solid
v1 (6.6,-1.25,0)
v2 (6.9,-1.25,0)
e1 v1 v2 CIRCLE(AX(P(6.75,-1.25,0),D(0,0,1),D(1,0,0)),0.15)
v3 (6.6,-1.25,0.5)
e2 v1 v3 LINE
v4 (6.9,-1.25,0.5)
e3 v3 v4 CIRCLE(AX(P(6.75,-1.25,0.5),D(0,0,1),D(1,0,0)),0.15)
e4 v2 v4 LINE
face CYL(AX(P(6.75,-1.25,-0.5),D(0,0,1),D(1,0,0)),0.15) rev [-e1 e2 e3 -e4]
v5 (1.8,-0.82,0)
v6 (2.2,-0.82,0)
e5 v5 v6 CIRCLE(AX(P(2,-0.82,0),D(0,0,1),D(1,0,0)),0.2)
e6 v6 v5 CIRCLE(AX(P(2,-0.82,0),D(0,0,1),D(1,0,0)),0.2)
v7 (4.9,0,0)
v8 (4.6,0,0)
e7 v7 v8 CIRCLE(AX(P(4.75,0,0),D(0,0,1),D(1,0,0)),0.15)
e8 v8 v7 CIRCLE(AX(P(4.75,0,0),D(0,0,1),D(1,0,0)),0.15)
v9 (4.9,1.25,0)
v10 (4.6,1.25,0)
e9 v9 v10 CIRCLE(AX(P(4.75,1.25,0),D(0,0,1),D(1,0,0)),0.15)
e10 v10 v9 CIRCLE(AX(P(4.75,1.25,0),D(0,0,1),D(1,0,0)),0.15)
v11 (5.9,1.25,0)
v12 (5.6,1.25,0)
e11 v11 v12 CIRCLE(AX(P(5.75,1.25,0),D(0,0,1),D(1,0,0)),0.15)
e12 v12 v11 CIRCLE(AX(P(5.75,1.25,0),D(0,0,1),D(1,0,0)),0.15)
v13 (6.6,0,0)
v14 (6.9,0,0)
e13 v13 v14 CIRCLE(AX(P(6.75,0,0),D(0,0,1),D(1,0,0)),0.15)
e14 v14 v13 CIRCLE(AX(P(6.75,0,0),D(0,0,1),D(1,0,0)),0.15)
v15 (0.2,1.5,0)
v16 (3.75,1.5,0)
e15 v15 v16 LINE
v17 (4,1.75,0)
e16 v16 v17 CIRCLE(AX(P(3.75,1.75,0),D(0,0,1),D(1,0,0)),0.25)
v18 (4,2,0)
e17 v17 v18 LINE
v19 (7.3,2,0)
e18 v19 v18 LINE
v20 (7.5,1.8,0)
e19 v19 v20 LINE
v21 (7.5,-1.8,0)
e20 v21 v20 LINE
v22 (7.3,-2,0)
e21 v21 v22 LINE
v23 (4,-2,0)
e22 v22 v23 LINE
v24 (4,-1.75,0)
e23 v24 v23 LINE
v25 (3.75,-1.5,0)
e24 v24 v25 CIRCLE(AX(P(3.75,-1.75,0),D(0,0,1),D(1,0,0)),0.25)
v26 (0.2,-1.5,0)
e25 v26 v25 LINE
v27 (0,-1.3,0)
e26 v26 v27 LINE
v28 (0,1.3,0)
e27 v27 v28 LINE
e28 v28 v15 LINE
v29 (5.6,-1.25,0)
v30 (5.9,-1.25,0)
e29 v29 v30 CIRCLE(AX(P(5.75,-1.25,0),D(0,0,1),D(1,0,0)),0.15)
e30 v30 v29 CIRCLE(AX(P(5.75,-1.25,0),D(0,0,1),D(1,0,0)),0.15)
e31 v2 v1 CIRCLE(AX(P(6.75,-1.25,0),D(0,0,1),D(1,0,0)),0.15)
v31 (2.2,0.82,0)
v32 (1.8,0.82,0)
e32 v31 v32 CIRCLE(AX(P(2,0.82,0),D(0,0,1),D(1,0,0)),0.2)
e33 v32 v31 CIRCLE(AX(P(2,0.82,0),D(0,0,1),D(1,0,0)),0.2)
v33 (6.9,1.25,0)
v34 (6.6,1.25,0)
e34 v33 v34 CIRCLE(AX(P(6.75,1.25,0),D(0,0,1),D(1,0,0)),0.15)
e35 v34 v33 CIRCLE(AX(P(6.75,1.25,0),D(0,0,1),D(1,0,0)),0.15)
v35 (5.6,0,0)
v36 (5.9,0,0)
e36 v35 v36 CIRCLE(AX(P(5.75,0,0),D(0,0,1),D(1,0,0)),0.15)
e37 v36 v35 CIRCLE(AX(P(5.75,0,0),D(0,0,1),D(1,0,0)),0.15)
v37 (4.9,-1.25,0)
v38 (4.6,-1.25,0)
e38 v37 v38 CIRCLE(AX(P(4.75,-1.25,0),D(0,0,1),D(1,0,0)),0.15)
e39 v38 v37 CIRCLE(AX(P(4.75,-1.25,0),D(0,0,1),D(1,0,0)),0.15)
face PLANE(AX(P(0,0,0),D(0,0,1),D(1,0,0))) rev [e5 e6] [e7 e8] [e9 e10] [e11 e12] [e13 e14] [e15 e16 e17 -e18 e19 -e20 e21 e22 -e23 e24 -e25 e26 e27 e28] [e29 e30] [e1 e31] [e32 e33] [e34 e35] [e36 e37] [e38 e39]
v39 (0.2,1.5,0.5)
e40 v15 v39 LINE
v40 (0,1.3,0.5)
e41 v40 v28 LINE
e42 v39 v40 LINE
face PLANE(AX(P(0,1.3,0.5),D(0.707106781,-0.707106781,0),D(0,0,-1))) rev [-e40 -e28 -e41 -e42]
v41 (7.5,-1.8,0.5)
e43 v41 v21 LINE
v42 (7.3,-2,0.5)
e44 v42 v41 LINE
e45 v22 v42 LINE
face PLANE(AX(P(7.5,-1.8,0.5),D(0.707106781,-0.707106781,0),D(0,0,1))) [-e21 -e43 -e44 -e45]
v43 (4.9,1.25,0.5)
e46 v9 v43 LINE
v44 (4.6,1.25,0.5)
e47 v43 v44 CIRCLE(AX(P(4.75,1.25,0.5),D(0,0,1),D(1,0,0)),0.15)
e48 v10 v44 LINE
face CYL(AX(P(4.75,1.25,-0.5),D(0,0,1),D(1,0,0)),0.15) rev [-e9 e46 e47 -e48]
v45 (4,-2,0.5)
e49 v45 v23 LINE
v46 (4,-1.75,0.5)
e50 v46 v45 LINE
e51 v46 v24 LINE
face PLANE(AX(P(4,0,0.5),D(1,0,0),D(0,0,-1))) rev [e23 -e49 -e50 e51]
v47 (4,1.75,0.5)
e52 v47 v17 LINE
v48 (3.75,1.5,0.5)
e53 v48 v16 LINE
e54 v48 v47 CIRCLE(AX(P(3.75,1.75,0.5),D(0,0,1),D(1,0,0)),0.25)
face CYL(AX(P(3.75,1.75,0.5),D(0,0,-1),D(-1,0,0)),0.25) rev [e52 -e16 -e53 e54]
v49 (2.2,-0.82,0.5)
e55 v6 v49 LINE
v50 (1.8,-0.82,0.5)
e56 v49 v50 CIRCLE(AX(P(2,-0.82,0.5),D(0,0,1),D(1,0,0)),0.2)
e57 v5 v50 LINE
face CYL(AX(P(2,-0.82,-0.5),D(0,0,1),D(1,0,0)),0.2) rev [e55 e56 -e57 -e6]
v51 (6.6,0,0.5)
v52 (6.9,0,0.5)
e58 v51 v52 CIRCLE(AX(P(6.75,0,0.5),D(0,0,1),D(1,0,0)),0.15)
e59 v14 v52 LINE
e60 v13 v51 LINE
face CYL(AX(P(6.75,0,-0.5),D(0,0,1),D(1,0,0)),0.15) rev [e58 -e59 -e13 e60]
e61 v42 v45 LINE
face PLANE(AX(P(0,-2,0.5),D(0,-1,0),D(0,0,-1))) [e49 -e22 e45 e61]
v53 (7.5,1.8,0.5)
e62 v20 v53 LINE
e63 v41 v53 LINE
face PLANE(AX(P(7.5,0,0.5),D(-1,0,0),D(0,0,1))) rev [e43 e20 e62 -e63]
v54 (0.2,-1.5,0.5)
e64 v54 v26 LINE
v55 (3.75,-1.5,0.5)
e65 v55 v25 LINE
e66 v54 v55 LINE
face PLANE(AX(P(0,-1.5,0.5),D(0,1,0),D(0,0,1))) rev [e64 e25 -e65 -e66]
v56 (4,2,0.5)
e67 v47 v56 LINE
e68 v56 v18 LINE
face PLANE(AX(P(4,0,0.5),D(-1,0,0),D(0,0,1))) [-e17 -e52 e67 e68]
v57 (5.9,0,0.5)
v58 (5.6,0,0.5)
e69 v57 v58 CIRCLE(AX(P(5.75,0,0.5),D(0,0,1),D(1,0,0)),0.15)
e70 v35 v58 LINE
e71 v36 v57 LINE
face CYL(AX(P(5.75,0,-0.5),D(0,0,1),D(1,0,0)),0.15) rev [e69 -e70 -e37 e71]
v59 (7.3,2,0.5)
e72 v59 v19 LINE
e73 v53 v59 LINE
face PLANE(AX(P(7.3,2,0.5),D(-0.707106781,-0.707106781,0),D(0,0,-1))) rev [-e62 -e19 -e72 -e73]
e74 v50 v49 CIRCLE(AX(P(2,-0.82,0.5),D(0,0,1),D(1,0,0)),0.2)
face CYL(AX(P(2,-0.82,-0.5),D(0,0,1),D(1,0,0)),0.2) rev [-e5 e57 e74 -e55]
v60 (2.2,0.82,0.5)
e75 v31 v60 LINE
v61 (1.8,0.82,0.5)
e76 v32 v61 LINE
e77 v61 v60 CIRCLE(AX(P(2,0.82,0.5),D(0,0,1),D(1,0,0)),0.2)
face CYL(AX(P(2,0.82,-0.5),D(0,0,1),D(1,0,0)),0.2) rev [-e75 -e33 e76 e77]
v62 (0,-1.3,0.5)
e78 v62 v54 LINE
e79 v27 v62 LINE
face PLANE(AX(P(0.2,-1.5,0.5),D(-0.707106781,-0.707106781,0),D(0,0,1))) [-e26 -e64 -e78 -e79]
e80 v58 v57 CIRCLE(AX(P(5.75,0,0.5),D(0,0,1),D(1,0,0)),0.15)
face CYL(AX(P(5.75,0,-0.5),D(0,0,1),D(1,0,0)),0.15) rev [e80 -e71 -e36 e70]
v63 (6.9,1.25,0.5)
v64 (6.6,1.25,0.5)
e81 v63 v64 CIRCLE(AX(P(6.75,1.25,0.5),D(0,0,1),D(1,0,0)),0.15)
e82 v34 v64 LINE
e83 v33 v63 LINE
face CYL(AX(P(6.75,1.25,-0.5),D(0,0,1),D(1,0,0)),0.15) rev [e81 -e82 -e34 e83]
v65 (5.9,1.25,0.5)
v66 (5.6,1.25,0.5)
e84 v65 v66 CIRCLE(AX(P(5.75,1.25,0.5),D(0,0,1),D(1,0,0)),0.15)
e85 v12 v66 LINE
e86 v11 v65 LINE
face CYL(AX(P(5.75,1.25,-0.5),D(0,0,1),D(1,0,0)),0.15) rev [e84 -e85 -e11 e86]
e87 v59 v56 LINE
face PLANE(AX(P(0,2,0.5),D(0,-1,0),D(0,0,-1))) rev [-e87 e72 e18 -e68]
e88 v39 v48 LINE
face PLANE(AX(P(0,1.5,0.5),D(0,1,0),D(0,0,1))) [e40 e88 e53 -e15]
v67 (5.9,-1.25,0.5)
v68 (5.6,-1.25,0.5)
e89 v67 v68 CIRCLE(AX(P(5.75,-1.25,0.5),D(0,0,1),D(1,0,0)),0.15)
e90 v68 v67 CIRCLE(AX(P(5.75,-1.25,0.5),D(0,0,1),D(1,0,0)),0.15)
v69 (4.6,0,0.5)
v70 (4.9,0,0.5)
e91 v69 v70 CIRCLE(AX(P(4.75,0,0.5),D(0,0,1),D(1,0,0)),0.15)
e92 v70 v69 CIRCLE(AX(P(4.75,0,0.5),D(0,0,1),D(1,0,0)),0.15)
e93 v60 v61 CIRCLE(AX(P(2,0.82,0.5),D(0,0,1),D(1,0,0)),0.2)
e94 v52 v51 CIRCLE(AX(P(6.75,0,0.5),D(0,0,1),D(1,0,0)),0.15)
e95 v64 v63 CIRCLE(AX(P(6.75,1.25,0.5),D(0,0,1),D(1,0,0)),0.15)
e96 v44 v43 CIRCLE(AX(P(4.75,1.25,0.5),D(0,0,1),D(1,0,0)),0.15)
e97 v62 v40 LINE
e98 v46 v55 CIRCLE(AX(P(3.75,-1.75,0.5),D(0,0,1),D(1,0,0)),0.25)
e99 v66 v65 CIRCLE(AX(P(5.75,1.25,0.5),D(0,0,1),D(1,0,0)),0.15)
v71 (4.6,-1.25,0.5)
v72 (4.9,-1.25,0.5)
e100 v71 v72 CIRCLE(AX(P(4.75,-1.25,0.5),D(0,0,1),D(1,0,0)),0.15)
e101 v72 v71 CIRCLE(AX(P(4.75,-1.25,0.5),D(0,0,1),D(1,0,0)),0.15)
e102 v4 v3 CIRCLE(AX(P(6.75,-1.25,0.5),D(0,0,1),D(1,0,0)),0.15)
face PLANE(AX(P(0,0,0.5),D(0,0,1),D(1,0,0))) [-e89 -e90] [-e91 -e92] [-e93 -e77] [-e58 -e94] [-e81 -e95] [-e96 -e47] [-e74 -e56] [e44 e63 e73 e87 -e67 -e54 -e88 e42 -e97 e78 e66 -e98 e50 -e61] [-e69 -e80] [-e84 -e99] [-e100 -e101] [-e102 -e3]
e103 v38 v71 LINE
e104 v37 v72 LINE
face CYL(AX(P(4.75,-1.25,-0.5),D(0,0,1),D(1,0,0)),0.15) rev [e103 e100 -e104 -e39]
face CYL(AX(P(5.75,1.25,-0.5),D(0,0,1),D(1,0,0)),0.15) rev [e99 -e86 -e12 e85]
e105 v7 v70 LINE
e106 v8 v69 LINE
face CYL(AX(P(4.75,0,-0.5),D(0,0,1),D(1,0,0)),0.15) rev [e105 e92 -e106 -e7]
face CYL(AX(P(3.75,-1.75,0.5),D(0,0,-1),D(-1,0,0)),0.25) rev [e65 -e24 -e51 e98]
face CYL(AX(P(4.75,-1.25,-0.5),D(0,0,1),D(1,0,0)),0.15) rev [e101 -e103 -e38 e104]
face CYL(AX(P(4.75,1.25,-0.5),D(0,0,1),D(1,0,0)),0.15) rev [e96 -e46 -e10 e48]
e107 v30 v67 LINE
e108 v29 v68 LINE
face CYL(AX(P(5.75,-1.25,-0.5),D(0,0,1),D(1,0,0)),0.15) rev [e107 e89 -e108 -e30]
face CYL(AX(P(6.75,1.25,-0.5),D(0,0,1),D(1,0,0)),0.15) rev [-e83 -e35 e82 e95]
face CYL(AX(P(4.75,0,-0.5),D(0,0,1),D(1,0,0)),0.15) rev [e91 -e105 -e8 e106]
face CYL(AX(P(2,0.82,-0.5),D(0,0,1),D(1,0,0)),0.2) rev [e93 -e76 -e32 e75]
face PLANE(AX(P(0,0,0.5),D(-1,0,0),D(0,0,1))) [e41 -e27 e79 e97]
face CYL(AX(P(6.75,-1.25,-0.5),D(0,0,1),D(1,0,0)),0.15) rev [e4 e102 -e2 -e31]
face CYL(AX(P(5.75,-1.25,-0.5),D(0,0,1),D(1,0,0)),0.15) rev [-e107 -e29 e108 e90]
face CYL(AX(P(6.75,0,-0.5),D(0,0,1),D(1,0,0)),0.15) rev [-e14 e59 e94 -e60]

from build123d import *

# Parameters (mm, degrees)
STEPPED_TAB_PLATE_0_5MM_DEPTH = 0.5
CORNER_CHAMFER_0_2X45_A_SIZE  = 0.2
CORNER_CHAMFER_0_2X45_B_SIZE  = 0.2
SCREW_HOLES_SKETCH_R          = 0.2
SCREW_HOLES_2X_DEPTH          = 1
HOLE_GRID_SKETCH_R            = 0.15
HOLE_GRID_3X3_DEPTH           = 1


with BuildPart() as part:
    # Stepped Tab Profile Sketch → Stepped Tab Plate 0.5mm (new body)
    with BuildSketch(Plane.XY):
        with BuildLine():
            ThreePointArc((3.75, 1.5), (3.926776695, 1.573223305), (4, 1.75))
            Line((4, 1.75), (4, 2))
            Line((4, 2), (7.5, 2))
            Line((7.5, 2), (7.5, 0))
            Line((7.5, 0), (0, 0))
            Line((0, 0), (0, 1.5))
            Line((0, 1.5), (3.75, 1.5))
        make_face()
        with BuildLine():
            ThreePointArc((4, -1.75), (3.926776695, -1.573223305), (3.75, -1.5))
            Line((3.75, -1.5), (0, -1.5))
            Line((0, -1.5), (0, 0))
            Line((0, 0), (7.5, 0))
            Line((7.5, 0), (7.5, -2))
            Line((7.5, -2), (4, -2))
            Line((4, -2), (4, -1.75))
        make_face()
    extrude(amount=STEPPED_TAB_PLATE_0_5MM_DEPTH)

    # Corner Chamfer 0.2x45 A
    corner_chamfer_0_2x45_a_edges = [part.edges().sort_by_distance(p)[0] for p in [
        (7.5, 2, 0.25),
        (0, 1.5, 0.25),
    ]]
    chamfer(corner_chamfer_0_2x45_a_edges, length=CORNER_CHAMFER_0_2X45_A_SIZE)

    # Corner Chamfer 0.2x45 B
    corner_chamfer_0_2x45_b_edges = [part.edges().sort_by_distance(p)[0] for p in [
        (7.5, -2, 0.25),
        (0, -1.5, 0.25),
    ]]
    chamfer(corner_chamfer_0_2x45_b_edges, length=CORNER_CHAMFER_0_2X45_B_SIZE)

    # Screw Holes Sketch → Screw Holes 2x (cut)
    with BuildSketch(Plane.XY.offset(0.5)):
        with Locations((2, 0.82)):
            Circle(SCREW_HOLES_SKETCH_R)
        with Locations((2, -0.82)):
            Circle(SCREW_HOLES_SKETCH_R)
    extrude(amount=-SCREW_HOLES_2X_DEPTH, mode=Mode.SUBTRACT)

    # Hole Grid Sketch → Hole Grid 3x3 (cut)
    with BuildSketch(Plane.XY.offset(0.5)):
        with Locations((4.75, 1.25)):
            Circle(HOLE_GRID_SKETCH_R)
        with Locations((5.75, 1.25)):
            Circle(HOLE_GRID_SKETCH_R)
        with Locations((6.75, 1.25)):
            Circle(HOLE_GRID_SKETCH_R)
        with Locations((6.75, 0)):
            Circle(HOLE_GRID_SKETCH_R)
        with Locations((6.75, -1.25)):
            Circle(HOLE_GRID_SKETCH_R)
        with Locations((5.75, -1.25)):
            Circle(HOLE_GRID_SKETCH_R)
        with Locations((4.75, -1.25)):
            Circle(HOLE_GRID_SKETCH_R)
        with Locations((4.75, 0)):
            Circle(HOLE_GRID_SKETCH_R)
        with Locations((5.75, 0)):
            Circle(HOLE_GRID_SKETCH_R)
    extrude(amount=-HOLE_GRID_3X3_DEPTH, mode=Mode.SUBTRACT)


solid = part.part
